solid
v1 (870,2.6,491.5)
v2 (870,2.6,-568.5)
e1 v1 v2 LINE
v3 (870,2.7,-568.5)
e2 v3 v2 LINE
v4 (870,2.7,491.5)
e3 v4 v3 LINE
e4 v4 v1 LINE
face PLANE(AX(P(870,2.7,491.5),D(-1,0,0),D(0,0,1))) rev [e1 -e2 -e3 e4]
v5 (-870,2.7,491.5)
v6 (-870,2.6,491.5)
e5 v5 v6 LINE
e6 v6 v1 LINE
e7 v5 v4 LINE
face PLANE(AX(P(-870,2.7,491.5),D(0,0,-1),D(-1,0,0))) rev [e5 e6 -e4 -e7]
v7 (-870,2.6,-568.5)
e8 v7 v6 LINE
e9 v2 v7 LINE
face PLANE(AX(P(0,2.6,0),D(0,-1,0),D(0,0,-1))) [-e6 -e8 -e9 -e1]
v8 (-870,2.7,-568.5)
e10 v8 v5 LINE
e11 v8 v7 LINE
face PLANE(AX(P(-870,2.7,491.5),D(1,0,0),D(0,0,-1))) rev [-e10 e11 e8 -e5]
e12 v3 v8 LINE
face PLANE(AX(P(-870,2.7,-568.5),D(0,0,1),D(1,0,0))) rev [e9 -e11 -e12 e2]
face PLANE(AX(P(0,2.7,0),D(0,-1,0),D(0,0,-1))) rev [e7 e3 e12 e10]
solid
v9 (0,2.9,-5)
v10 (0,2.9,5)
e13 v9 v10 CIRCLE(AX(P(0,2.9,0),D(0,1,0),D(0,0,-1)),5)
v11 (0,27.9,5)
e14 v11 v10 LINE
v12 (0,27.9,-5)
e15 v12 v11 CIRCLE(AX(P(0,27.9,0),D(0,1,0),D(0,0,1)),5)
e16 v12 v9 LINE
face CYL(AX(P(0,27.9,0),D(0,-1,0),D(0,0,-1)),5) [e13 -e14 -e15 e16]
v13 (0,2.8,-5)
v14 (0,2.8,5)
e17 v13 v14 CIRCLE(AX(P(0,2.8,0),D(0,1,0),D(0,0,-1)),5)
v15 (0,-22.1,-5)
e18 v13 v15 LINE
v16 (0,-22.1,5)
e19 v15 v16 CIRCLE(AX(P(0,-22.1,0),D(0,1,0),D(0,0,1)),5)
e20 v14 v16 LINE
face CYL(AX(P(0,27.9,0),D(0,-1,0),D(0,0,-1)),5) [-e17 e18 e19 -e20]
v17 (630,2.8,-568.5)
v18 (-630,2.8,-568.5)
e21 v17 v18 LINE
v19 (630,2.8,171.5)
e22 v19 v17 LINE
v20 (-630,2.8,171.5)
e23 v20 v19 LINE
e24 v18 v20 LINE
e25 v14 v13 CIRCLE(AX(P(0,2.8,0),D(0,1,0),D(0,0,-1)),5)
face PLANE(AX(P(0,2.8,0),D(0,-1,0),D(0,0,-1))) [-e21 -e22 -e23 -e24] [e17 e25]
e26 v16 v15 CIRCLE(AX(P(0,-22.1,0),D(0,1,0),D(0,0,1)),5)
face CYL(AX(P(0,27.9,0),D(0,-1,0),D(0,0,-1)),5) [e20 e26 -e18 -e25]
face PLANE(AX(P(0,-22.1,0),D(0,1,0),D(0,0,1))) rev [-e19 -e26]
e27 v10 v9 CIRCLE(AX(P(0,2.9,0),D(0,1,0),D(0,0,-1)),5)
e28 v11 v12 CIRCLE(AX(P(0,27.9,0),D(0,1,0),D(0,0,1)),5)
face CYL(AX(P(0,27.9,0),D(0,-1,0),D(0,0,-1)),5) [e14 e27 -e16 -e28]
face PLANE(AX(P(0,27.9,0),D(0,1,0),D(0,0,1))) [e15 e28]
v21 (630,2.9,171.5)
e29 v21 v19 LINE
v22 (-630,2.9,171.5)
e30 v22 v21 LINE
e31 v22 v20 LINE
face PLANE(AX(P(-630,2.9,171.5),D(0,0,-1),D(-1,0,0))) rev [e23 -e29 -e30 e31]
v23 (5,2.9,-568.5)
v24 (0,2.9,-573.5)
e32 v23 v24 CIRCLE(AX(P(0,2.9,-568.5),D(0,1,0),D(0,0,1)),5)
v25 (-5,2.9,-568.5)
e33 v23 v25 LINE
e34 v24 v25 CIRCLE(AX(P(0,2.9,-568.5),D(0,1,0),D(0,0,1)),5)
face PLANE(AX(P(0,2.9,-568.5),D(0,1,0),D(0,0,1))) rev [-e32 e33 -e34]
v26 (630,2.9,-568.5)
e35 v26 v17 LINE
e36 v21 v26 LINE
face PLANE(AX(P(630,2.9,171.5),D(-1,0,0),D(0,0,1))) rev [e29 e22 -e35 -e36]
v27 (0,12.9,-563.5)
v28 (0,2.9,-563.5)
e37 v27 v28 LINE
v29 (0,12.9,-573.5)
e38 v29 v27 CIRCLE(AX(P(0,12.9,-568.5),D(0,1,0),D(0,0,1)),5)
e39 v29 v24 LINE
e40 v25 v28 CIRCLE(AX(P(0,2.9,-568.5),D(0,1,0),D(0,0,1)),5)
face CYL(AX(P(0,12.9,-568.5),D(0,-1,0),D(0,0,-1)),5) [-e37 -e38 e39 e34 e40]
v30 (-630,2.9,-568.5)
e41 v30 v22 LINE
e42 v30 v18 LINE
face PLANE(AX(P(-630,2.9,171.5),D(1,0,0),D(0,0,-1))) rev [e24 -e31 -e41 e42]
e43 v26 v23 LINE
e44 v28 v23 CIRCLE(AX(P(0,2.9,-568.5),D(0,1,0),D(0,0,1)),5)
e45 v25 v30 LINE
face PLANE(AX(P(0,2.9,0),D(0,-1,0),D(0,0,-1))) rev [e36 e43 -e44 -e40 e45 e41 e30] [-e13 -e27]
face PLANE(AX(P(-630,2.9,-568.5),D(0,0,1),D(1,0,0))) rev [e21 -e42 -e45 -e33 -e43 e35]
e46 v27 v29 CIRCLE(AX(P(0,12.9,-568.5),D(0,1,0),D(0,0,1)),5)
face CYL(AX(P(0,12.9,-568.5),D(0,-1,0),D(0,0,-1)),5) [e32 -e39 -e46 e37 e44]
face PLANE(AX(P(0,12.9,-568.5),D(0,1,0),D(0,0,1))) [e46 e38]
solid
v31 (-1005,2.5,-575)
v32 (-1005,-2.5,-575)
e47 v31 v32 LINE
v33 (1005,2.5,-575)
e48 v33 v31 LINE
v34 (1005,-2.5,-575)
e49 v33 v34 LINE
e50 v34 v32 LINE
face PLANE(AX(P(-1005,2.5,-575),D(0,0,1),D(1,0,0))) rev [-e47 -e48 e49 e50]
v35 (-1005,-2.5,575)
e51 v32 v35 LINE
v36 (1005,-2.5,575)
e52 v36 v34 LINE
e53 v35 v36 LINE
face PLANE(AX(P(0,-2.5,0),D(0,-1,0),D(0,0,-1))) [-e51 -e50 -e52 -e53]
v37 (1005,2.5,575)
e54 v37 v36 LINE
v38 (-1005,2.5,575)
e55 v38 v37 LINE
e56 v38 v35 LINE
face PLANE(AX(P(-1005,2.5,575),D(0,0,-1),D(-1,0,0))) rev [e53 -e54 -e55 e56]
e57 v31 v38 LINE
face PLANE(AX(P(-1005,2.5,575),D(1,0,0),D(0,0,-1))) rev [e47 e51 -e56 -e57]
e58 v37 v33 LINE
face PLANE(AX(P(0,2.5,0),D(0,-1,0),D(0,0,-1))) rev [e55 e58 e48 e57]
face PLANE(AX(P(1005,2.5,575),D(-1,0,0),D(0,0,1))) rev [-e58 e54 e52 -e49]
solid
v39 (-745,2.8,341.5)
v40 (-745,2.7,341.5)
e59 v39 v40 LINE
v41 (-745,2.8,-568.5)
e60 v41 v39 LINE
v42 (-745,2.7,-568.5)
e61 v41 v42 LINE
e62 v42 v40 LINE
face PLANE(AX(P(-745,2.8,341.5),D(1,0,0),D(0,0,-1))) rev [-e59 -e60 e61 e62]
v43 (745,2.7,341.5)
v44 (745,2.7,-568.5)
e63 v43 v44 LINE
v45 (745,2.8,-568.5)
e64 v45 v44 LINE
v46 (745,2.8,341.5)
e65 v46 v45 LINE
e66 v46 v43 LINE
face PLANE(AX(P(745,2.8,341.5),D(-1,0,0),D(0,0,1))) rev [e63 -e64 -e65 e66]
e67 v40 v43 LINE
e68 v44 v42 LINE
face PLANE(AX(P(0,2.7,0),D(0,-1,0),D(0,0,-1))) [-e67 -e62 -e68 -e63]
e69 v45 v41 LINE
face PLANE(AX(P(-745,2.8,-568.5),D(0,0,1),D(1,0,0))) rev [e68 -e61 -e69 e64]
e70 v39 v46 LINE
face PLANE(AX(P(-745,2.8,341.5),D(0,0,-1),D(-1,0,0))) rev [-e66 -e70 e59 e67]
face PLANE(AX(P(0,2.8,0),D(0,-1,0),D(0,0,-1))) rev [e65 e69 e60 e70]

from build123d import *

# Parameters (mm, degrees)
SKETCH_1_W      = 2010
SKETCH_1_H      = 1150
EXTRUDE_1_DEPTH = 2.5
SKETCH_3_W      = 1740
SKETCH_3_H      = 1060
EXTRUDE_5_DEPTH = 0.1
SKETCH_4_W      = 1490
SKETCH_4_H      = 910
EXTRUDE_6_DEPTH = 0.1
SKETCH_5_W      = 1260
SKETCH_5_H      = 740
EXTRUDE_7_DEPTH = 0.1
SKETCH_6_R      = 5
EXTRUDE_8_DEPTH = 25
SKETCH_7_R      = 5
EXTRUDE_9_DEPTH = 10


with BuildPart() as part:
    # 草图1 → 凸台-拉伸1 (new, symmetric)
    with BuildSketch(Plane(origin=(0, 0, 0), x_dir=(1, 0, 0), z_dir=(0, 1, 0))):
        Rectangle(SKETCH_1_W, SKETCH_1_H)
    extrude(amount=EXTRUDE_1_DEPTH, both=True)


with BuildPart() as body_2:
    # 草图3 → 凸台-拉伸5 (new body)
    with BuildSketch(Plane(origin=(0, 2.6, 0), x_dir=(1, 0, 0), z_dir=(0, 1, 0))):
        with Locations((0, 38.5)):
            Rectangle(SKETCH_3_W, SKETCH_3_H)
    extrude(amount=EXTRUDE_5_DEPTH)


with BuildPart() as body_3:
    # 草图4 → 凸台-拉伸6 (new body)
    with BuildSketch(Plane(origin=(0, 2.7, 0), x_dir=(1, 0, 0), z_dir=(0, 1, 0))):
        with Locations((0, 113.5)):
            Rectangle(SKETCH_4_W, SKETCH_4_H)
    extrude(amount=EXTRUDE_6_DEPTH)


with BuildPart() as body_4:
    # 草图5 → 凸台-拉伸7 (new body)
    with BuildSketch(Plane(origin=(0, 2.8, 0), x_dir=(1, 0, 0), z_dir=(0, 1, 0))):
        with Locations((0, 198.5)):
            Rectangle(SKETCH_5_W, SKETCH_5_H)
    extrude(amount=EXTRUDE_7_DEPTH)

    # 草图6 → 凸台-拉伸8 (add, symmetric)
    with BuildSketch(Plane(origin=(0, 2.9, 0), x_dir=(1, 0, 0), z_dir=(0, 1, 0))):
        with Locations(Location((0, 0, 0), (0, 0, 90))):
            Circle(SKETCH_6_R)
    extrude(amount=EXTRUDE_8_DEPTH, both=True)

    # 草图7 → 凸台-拉伸9 (add)
    with BuildSketch(Plane(origin=(0, 2.9, 0), x_dir=(1, 0, 0), z_dir=(0, 1, 0))):
        with Locations(Location((0, 568.5, 0), (0, 0, 180))):
            Circle(SKETCH_7_R)
    extrude(amount=EXTRUDE_9_DEPTH)


solid = Compound([part.part, body_2.part, body_3.part, body_4.part])
